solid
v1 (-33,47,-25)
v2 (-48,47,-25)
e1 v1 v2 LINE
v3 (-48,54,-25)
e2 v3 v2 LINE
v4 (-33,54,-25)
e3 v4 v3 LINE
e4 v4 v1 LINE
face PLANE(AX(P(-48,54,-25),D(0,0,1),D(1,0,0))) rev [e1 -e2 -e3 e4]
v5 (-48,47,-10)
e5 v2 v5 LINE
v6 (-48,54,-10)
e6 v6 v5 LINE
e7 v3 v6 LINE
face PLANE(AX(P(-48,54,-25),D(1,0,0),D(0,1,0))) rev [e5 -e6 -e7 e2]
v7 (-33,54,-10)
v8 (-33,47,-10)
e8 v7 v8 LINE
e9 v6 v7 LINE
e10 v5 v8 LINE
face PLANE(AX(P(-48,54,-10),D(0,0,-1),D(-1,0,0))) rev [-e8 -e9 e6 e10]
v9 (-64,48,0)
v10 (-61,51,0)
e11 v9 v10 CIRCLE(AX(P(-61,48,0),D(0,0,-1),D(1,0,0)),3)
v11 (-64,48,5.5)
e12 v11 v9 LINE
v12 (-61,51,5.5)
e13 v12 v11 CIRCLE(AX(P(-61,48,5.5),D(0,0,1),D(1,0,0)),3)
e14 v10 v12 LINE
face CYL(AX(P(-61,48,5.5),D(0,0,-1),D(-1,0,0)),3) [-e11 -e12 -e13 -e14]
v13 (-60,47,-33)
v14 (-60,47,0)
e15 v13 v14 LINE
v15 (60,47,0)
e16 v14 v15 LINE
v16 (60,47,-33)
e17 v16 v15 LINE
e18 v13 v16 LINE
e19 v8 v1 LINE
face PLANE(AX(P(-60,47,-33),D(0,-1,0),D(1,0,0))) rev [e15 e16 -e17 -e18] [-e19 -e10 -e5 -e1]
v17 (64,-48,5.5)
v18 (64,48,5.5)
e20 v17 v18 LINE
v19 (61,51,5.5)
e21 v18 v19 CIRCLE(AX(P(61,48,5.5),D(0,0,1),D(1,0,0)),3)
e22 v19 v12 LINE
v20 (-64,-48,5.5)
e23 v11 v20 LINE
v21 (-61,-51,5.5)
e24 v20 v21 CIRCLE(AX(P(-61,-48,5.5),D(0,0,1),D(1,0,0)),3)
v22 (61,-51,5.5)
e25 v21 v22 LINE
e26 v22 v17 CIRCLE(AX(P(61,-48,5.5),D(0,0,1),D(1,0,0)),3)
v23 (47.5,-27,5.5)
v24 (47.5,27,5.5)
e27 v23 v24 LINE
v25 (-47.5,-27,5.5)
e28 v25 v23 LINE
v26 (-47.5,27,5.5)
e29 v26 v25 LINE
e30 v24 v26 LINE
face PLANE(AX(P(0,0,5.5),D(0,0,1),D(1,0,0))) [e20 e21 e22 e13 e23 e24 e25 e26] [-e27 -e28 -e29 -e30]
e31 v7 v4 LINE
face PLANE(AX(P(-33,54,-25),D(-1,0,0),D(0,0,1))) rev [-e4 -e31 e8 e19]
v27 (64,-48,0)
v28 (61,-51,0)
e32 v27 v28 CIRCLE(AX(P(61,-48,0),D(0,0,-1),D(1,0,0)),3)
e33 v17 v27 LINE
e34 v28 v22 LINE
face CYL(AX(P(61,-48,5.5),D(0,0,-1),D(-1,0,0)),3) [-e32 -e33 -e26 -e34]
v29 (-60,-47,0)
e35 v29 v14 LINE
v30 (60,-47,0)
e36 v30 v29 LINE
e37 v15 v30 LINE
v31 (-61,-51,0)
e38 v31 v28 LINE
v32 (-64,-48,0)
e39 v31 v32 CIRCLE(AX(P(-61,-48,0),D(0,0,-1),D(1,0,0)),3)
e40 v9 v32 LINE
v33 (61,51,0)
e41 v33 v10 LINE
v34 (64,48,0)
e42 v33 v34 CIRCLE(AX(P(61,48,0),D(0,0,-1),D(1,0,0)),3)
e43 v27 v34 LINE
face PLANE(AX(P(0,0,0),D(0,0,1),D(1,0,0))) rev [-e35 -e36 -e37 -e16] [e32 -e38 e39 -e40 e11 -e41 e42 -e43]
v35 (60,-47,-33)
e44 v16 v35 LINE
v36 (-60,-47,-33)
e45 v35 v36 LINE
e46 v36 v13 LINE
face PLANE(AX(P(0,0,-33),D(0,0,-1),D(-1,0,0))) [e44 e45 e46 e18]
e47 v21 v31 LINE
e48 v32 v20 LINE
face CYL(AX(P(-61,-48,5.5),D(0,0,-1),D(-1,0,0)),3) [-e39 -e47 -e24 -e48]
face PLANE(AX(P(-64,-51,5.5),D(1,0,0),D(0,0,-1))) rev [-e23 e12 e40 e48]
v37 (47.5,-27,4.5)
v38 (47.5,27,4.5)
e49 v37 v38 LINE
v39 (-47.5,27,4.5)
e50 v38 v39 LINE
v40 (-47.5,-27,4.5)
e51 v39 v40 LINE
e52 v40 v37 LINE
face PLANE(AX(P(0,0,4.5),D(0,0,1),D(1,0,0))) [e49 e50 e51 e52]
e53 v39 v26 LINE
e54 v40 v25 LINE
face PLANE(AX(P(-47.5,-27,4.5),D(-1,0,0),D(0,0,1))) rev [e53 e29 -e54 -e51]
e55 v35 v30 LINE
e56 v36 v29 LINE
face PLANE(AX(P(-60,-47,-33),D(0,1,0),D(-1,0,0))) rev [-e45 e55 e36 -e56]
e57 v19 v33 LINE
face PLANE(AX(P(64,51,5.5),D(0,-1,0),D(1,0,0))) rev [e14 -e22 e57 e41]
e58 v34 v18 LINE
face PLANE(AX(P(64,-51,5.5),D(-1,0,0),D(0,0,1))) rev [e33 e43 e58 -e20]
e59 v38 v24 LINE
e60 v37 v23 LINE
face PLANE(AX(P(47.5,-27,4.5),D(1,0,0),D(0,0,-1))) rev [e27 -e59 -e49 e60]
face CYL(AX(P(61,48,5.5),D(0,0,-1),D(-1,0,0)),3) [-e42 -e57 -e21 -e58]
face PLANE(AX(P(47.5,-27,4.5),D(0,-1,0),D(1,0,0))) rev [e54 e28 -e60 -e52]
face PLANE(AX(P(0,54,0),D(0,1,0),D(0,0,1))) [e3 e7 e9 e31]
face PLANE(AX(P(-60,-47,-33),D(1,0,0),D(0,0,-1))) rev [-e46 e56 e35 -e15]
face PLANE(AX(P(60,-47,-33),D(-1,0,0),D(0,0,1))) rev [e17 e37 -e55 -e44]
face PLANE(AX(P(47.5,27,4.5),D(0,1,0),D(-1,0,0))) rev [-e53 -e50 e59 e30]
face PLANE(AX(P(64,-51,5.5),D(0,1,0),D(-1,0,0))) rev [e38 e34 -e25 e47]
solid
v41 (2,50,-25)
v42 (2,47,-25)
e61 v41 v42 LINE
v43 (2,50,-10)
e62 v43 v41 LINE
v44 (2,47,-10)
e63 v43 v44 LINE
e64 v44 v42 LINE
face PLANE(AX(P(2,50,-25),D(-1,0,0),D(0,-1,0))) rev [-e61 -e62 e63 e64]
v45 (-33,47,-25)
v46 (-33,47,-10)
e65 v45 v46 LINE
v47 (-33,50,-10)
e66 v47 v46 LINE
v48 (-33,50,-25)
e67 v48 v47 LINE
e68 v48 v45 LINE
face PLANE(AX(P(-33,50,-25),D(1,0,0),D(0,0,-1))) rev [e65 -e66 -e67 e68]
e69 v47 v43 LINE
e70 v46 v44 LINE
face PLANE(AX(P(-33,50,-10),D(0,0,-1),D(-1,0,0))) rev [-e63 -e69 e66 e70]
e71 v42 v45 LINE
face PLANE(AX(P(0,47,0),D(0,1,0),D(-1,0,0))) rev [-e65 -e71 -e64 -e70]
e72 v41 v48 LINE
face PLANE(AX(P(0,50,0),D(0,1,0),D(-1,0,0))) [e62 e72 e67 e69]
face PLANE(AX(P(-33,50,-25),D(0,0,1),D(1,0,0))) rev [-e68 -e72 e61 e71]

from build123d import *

# Parameters (mm, degrees)
SKETCH1_W           = 128
SKETCH1_H           = 102
BOSS_EXTRUDE1_DEPTH = 5.5
SKETCH2_W           = 95
SKETCH2_H           = 54
CUT_EXTRUDE1_DEPTH  = 1
SKETCH3_W           = 120
SKETCH3_H           = 94
BOSS_EXTRUDE2_DEPTH = 33
FILLET1_R           = 3
SKETCH4_W           = 15
SKETCH4_H           = 15
BOSS_EXTRUDE3_DEPTH = 7
SKETCH5_W           = 35
SKETCH5_H           = 15
BOSS_EXTRUDE4_DEPTH = 3


with BuildPart() as part:
    # Sketch1 → Boss-Extrude1 (new body)
    with BuildSketch(Plane.XY):
        Rectangle(SKETCH1_W, SKETCH1_H)
    extrude(amount=BOSS_EXTRUDE1_DEPTH)

    # Sketch2 → Cut-Extrude1 (cut)
    with BuildSketch(Plane.XY.offset(5.5)):
        Rectangle(SKETCH2_W, SKETCH2_H)
    extrude(amount=-CUT_EXTRUDE1_DEPTH, mode=Mode.SUBTRACT)

    # Sketch3 → Boss-Extrude2 (add)
    with BuildSketch(Plane(origin=(0, 0, 0), x_dir=(-1, 0, 0), z_dir=(0, 0, -1))):
        Rectangle(SKETCH3_W, SKETCH3_H)
    extrude(amount=BOSS_EXTRUDE2_DEPTH)

    # Fillet1
    fillet1_edges = [part.edges().sort_by_distance(p)[0] for p in [
        (-64, 51, 2.75),
        (64, 51, 2.75),
        (64, -51, 2.75),
        (-64, -51, 2.75),
    ]]
    fillet(fillet1_edges, radius=FILLET1_R)

    # Sketch4 → Boss-Extrude3 (add)
    with BuildSketch(Plane(origin=(0, 47, 0), x_dir=(1, 0, 0), z_dir=(0, 1, 0))):
        with Locations((-40.5, 17.5)):
            Rectangle(SKETCH4_W, SKETCH4_H)
    extrude(amount=BOSS_EXTRUDE3_DEPTH)


with BuildPart() as body_2:
    # Sketch5 → Boss-Extrude4 (new body)
    with BuildSketch(Plane(origin=(0, 47, 0), x_dir=(1, 0, 0), z_dir=(0, 1, 0))):
        with Locations((-15.5, 17.5)):
            Rectangle(SKETCH5_W, SKETCH5_H)
    extrude(amount=BOSS_EXTRUDE4_DEPTH)


solid = Compound([part.part, body_2.part])
